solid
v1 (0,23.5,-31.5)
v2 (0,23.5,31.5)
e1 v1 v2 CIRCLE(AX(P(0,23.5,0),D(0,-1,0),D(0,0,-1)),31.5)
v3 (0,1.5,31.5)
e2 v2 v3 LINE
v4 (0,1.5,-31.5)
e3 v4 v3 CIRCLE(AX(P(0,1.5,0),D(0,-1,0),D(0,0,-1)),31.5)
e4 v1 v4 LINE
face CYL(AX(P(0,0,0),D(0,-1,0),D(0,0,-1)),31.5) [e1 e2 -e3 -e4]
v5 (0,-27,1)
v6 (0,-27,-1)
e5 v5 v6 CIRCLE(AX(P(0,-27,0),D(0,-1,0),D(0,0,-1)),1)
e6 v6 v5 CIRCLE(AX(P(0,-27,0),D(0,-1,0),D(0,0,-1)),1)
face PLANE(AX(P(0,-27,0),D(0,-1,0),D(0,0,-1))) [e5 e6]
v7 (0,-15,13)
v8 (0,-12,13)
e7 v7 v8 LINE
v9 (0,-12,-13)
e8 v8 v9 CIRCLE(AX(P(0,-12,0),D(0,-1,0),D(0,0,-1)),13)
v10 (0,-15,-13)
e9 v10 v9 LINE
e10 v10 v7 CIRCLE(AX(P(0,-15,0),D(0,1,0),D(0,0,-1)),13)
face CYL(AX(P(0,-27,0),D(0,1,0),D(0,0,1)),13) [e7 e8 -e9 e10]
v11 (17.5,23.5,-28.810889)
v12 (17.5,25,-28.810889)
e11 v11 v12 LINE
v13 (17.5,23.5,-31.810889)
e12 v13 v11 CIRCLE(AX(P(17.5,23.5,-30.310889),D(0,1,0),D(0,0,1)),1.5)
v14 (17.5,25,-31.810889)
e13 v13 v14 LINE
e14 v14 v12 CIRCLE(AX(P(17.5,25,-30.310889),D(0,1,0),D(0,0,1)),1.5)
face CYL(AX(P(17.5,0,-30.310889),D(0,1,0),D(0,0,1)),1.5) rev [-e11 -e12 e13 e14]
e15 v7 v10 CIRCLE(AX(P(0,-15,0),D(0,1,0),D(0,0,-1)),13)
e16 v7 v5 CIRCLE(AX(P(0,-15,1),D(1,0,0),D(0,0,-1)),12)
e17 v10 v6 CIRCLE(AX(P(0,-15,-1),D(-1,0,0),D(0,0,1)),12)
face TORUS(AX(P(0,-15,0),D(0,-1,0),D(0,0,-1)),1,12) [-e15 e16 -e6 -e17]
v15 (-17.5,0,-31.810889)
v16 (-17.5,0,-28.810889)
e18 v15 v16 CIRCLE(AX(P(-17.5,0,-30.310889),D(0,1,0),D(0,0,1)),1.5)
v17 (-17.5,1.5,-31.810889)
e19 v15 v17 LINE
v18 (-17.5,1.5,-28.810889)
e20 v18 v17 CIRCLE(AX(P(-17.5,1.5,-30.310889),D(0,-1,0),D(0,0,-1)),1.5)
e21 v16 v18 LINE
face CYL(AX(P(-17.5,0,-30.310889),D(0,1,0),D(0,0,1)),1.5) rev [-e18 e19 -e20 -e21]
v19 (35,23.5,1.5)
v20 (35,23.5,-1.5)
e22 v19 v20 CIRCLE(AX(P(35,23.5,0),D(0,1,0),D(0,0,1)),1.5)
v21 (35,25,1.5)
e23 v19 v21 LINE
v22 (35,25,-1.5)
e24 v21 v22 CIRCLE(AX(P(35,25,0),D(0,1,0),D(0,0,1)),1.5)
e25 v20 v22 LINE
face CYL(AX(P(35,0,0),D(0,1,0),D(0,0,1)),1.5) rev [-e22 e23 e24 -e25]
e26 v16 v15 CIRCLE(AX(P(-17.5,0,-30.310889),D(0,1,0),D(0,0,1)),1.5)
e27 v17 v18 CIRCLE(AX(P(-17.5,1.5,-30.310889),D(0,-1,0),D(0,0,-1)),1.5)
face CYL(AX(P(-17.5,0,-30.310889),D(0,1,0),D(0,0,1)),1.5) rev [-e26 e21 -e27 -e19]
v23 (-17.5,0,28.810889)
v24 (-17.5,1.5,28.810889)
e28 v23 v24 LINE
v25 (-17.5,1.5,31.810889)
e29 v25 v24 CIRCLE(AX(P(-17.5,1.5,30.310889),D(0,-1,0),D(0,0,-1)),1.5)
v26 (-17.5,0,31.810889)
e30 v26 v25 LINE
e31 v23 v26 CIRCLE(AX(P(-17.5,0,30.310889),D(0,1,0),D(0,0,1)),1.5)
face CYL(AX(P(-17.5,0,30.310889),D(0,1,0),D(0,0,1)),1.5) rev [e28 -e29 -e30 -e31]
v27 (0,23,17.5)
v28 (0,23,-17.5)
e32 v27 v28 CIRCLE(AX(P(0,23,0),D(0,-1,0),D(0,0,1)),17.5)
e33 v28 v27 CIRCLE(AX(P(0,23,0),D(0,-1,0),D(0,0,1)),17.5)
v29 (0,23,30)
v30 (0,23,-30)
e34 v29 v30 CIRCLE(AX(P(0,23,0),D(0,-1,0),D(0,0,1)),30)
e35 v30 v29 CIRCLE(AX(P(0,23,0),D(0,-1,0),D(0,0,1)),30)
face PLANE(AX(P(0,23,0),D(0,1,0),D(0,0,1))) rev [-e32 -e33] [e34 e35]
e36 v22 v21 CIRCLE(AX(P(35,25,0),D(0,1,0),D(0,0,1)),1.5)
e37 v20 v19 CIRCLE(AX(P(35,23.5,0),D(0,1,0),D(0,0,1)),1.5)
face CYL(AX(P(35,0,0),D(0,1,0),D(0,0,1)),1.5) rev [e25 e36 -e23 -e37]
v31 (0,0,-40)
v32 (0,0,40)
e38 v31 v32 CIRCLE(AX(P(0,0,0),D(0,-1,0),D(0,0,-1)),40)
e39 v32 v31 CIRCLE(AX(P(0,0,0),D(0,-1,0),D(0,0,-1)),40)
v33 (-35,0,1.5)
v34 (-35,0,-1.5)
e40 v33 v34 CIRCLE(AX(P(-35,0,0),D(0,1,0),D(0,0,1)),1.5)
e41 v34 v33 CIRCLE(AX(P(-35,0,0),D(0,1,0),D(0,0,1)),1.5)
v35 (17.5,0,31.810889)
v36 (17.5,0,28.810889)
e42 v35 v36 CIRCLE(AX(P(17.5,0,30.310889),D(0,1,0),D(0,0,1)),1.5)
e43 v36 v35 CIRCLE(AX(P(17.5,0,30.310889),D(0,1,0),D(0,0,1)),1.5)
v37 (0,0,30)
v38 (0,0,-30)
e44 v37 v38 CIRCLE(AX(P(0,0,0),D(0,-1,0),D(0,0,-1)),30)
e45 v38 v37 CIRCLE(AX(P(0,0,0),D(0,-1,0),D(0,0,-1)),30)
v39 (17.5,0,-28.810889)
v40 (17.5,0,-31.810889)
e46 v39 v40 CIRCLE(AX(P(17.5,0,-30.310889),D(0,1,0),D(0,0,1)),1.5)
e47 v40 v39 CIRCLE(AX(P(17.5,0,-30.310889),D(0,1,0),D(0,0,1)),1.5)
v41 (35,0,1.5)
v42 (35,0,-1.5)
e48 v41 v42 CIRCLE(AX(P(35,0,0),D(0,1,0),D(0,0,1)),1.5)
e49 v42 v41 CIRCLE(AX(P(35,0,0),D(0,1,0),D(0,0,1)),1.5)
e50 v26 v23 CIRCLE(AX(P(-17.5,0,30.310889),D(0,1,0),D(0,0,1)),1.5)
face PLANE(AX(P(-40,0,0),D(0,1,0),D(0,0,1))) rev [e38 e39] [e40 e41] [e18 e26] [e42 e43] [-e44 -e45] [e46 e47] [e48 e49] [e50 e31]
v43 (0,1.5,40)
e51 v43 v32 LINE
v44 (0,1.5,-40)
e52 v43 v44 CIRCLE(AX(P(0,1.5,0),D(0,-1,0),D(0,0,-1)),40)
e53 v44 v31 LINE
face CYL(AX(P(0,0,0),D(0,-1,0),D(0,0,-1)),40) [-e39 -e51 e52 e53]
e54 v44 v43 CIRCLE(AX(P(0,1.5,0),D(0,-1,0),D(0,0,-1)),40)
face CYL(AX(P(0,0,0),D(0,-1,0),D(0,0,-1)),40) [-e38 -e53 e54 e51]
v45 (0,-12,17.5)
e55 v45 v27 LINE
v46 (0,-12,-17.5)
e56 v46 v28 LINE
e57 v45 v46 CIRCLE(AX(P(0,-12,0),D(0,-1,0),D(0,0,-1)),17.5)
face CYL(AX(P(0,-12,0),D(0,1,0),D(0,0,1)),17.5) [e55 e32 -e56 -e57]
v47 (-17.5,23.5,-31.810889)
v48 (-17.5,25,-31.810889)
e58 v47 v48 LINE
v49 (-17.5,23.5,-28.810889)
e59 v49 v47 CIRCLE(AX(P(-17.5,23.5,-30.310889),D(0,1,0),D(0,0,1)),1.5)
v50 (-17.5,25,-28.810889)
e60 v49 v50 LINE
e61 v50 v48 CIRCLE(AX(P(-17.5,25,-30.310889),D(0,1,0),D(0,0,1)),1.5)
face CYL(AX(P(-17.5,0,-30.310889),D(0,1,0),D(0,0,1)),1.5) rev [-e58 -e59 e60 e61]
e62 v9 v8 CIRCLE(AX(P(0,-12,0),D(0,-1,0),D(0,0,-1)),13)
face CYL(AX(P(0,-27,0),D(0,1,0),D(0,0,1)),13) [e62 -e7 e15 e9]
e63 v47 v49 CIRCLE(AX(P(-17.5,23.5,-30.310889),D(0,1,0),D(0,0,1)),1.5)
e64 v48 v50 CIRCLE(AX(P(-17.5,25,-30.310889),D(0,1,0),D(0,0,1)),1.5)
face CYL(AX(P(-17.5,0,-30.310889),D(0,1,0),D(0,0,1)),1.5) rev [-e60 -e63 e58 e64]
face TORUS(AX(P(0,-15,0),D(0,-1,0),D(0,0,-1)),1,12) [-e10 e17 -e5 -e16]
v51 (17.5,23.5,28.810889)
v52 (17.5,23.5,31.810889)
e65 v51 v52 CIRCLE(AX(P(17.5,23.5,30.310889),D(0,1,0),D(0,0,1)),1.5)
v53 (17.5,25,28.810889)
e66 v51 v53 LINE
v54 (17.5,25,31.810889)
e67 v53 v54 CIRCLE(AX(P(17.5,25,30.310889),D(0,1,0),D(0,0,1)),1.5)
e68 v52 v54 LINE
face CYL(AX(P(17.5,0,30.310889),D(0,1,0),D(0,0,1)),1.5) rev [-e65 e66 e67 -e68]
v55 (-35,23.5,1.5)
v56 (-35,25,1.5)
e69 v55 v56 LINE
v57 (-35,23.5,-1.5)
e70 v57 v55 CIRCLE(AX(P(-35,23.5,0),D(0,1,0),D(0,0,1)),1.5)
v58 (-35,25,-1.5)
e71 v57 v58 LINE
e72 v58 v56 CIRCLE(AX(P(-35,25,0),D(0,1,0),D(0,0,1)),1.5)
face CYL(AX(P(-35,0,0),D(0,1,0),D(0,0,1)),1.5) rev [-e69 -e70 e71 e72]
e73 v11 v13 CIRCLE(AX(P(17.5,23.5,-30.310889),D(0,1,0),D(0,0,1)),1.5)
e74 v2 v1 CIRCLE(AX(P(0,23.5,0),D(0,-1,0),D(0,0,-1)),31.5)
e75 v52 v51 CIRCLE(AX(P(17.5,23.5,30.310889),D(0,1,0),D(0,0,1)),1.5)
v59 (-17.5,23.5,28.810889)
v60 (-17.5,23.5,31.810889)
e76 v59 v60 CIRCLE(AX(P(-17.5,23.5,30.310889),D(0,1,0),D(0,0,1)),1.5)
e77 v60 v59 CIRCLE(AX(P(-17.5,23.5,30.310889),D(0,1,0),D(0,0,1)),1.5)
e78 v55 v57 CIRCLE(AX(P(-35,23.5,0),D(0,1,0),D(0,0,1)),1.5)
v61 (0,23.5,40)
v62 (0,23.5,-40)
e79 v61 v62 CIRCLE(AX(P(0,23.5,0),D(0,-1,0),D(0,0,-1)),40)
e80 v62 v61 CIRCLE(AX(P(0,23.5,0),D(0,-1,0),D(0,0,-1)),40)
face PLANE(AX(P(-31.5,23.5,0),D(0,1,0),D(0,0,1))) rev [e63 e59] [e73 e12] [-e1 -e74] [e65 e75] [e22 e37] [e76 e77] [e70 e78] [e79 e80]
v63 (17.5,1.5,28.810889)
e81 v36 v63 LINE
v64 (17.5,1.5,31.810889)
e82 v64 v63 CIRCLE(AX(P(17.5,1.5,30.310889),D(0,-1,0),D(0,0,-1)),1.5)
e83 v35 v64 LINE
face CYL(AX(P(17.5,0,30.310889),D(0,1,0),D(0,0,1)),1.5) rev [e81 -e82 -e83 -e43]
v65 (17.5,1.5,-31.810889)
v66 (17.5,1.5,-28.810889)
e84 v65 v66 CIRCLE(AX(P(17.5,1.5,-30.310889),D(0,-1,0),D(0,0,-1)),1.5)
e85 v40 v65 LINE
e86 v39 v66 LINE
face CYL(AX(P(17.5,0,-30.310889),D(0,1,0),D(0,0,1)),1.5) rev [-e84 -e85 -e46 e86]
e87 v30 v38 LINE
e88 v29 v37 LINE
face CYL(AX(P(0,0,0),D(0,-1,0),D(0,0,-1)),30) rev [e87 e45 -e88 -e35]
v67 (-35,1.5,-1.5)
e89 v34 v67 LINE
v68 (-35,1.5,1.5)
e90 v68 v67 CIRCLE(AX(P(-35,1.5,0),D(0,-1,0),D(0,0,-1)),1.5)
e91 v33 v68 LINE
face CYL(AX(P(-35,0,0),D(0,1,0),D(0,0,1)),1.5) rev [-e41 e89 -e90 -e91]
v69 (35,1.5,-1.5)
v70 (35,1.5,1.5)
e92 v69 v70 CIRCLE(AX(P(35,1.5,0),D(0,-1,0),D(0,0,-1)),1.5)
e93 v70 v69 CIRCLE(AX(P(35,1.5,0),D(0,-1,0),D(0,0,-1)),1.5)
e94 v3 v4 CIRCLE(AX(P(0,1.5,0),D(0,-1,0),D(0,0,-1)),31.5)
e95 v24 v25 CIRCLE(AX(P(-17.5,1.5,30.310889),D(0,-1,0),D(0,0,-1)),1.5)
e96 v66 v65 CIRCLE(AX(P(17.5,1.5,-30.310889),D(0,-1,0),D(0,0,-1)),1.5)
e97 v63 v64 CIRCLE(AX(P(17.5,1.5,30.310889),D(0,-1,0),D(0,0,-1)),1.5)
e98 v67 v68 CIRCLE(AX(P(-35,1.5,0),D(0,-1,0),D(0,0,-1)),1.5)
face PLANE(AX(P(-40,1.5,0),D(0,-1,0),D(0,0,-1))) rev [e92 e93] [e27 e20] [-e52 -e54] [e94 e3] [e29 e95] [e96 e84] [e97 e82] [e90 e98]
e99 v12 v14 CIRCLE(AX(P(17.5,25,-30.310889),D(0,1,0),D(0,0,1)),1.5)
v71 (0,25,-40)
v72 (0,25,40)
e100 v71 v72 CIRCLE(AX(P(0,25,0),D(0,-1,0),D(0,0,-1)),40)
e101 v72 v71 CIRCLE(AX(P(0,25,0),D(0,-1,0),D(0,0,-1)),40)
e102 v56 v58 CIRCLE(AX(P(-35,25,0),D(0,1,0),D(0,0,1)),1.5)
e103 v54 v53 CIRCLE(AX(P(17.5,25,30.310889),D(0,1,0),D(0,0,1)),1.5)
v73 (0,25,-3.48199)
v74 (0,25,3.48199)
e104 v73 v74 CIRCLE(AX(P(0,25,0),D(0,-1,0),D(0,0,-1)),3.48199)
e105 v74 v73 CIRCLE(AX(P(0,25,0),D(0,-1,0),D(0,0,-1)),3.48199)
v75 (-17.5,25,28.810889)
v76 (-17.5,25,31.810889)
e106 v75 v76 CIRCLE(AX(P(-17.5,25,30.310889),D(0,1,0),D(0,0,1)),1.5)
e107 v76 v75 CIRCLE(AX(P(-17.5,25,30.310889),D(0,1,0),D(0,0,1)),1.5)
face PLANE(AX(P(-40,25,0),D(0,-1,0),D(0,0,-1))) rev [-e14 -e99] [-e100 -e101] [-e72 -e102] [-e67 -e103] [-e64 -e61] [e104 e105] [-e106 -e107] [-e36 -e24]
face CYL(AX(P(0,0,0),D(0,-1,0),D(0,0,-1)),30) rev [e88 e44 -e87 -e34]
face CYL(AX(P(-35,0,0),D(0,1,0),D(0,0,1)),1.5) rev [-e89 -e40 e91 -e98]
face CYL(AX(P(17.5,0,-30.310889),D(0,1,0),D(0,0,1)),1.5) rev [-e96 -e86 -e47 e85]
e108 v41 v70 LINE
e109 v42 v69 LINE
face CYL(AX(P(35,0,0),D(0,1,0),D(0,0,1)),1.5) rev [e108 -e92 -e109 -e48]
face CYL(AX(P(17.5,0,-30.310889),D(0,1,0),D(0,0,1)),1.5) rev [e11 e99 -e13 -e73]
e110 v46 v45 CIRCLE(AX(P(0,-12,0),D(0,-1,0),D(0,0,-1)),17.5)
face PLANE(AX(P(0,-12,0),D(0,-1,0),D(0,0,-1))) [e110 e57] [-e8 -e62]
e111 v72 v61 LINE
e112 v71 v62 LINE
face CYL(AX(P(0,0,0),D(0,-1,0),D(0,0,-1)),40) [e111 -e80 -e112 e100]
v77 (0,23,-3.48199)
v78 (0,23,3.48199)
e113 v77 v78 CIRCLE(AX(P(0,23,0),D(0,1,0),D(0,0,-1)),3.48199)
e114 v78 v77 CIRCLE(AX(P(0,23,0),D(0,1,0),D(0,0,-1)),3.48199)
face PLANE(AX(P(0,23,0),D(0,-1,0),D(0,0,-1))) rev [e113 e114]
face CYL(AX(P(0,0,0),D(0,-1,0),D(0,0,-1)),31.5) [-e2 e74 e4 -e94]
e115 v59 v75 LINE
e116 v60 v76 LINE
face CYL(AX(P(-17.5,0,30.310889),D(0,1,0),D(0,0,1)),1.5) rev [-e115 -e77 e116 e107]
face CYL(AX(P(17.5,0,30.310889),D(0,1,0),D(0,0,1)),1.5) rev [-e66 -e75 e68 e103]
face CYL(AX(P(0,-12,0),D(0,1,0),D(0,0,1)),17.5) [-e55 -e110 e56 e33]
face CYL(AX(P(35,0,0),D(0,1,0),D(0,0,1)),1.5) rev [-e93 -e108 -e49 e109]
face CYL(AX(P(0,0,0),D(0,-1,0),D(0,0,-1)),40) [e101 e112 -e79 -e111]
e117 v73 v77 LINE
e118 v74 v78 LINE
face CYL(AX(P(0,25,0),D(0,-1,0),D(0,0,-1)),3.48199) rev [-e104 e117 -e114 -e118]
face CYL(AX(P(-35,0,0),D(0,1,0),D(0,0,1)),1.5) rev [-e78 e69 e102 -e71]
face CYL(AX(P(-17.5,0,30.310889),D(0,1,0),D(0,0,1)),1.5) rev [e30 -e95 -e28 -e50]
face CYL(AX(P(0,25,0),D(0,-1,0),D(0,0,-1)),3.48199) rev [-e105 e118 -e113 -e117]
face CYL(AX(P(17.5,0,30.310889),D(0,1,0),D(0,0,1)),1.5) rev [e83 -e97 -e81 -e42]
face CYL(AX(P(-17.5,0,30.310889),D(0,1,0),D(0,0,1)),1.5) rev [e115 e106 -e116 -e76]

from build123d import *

# Parameters (mm, degrees)
SKETCH2_R           = 1.5
CUT_EXTRUDE1_DEPTH  = 62.846584384
SKETCH3_R           = 30
BOSS_EXTRUDE1_DEPTH = 2
SKETCH4_R           = 3.481990468
CUT_EXTRUDE2_DEPTH  = 2
SKETCH5_R           = 17.5
BOSS_EXTRUDE2_DEPTH = 35
SKETCH6_R           = 13
BOSS_EXTRUDE3_DEPTH = 15
FILLET1_R           = 12


with BuildPart() as part:
    # Sketch1 → Revolve1 (revolve)
    with BuildSketch(Plane.XY, mode=Mode.PRIVATE) as revolve1_sk:
        Polygon((-40, 0), (-30, 0), (-30, 25), (-40, 25), (-40, 23.5), (-31.5, 23.5), (-31.5, 1.5), (-40, 1.5), align=None)
    revolve(revolve1_sk.sketch.rotate(Axis((0, 0, 0), (0, 1, 0)), 270), axis=Axis((0, 0, 0), (0, 1, 0)))

    # Sketch2 → Cut-Extrude1 (cut, through all)
    with BuildSketch(Plane(origin=(0, 25, 0), x_dir=(1, 0, 0), z_dir=(0, 1, 0))):
        with Locations(Location((-35, 0, 0), (0, 0, 270))):
            Circle(SKETCH2_R)
        with Locations(Location((-17.5, 30.310889132, 0), (0, 0, 270))):
            Circle(SKETCH2_R)
        with Locations(Location((17.5, 30.310889132, 0), (0, 0, 270))):
            Circle(SKETCH2_R)
        with Locations(Location((35, 0, 0), (0, 0, 270))):
            Circle(SKETCH2_R)
        with Locations(Location((17.5, -30.310889132, 0), (0, 0, 270))):
            Circle(SKETCH2_R)
        with Locations(Location((-17.5, -30.310889132, 0), (0, 0, 270))):
            Circle(SKETCH2_R)
    extrude(amount=-CUT_EXTRUDE1_DEPTH, mode=Mode.SUBTRACT)

    # Sketch3 → Boss-Extrude1 (add)
    with BuildSketch(Plane(origin=(0, 25, 0), x_dir=(1, 0, 0), z_dir=(0, 1, 0))):
        with Locations(Location((0, 0, 0), (0, 0, 90))):
            Circle(SKETCH3_R)
    extrude(amount=-BOSS_EXTRUDE1_DEPTH)

    # Sketch4 → Cut-Extrude2 (cut)
    with BuildSketch(Plane(origin=(0, 23, 0), x_dir=(-1, 0, 0), z_dir=(0, -1, 0))):
        with Locations(Location((0, 0, 0), (0, 0, 90))):
            Circle(SKETCH4_R)
    extrude(amount=-CUT_EXTRUDE2_DEPTH, mode=Mode.SUBTRACT)

    # Sketch5 → Boss-Extrude2 (add)
    with BuildSketch(Plane(origin=(0, 23, 0), x_dir=(-1, 0, 0), z_dir=(0, -1, 0))):
        with Locations(Location((0, 0, 0), (0, 0, 270))):
            Circle(SKETCH5_R)
    extrude(amount=BOSS_EXTRUDE2_DEPTH)

    # Sketch6 → Boss-Extrude3 (add)
    with BuildSketch(Plane(origin=(0, -12, 0), x_dir=(-1, 0, 0), z_dir=(0, -1, 0))):
        with Locations(Location((0, 0, 0), (0, 0, 90))):
            Circle(SKETCH6_R)
    extrude(amount=BOSS_EXTRUDE3_DEPTH)

    # Fillet1
    fillet1_edges = [part.edges().sort_by_distance(p)[0] for p in [
        (0, -27, 13),
    ]]
    fillet(fillet1_edges, radius=FILLET1_R)


solid = part.part
